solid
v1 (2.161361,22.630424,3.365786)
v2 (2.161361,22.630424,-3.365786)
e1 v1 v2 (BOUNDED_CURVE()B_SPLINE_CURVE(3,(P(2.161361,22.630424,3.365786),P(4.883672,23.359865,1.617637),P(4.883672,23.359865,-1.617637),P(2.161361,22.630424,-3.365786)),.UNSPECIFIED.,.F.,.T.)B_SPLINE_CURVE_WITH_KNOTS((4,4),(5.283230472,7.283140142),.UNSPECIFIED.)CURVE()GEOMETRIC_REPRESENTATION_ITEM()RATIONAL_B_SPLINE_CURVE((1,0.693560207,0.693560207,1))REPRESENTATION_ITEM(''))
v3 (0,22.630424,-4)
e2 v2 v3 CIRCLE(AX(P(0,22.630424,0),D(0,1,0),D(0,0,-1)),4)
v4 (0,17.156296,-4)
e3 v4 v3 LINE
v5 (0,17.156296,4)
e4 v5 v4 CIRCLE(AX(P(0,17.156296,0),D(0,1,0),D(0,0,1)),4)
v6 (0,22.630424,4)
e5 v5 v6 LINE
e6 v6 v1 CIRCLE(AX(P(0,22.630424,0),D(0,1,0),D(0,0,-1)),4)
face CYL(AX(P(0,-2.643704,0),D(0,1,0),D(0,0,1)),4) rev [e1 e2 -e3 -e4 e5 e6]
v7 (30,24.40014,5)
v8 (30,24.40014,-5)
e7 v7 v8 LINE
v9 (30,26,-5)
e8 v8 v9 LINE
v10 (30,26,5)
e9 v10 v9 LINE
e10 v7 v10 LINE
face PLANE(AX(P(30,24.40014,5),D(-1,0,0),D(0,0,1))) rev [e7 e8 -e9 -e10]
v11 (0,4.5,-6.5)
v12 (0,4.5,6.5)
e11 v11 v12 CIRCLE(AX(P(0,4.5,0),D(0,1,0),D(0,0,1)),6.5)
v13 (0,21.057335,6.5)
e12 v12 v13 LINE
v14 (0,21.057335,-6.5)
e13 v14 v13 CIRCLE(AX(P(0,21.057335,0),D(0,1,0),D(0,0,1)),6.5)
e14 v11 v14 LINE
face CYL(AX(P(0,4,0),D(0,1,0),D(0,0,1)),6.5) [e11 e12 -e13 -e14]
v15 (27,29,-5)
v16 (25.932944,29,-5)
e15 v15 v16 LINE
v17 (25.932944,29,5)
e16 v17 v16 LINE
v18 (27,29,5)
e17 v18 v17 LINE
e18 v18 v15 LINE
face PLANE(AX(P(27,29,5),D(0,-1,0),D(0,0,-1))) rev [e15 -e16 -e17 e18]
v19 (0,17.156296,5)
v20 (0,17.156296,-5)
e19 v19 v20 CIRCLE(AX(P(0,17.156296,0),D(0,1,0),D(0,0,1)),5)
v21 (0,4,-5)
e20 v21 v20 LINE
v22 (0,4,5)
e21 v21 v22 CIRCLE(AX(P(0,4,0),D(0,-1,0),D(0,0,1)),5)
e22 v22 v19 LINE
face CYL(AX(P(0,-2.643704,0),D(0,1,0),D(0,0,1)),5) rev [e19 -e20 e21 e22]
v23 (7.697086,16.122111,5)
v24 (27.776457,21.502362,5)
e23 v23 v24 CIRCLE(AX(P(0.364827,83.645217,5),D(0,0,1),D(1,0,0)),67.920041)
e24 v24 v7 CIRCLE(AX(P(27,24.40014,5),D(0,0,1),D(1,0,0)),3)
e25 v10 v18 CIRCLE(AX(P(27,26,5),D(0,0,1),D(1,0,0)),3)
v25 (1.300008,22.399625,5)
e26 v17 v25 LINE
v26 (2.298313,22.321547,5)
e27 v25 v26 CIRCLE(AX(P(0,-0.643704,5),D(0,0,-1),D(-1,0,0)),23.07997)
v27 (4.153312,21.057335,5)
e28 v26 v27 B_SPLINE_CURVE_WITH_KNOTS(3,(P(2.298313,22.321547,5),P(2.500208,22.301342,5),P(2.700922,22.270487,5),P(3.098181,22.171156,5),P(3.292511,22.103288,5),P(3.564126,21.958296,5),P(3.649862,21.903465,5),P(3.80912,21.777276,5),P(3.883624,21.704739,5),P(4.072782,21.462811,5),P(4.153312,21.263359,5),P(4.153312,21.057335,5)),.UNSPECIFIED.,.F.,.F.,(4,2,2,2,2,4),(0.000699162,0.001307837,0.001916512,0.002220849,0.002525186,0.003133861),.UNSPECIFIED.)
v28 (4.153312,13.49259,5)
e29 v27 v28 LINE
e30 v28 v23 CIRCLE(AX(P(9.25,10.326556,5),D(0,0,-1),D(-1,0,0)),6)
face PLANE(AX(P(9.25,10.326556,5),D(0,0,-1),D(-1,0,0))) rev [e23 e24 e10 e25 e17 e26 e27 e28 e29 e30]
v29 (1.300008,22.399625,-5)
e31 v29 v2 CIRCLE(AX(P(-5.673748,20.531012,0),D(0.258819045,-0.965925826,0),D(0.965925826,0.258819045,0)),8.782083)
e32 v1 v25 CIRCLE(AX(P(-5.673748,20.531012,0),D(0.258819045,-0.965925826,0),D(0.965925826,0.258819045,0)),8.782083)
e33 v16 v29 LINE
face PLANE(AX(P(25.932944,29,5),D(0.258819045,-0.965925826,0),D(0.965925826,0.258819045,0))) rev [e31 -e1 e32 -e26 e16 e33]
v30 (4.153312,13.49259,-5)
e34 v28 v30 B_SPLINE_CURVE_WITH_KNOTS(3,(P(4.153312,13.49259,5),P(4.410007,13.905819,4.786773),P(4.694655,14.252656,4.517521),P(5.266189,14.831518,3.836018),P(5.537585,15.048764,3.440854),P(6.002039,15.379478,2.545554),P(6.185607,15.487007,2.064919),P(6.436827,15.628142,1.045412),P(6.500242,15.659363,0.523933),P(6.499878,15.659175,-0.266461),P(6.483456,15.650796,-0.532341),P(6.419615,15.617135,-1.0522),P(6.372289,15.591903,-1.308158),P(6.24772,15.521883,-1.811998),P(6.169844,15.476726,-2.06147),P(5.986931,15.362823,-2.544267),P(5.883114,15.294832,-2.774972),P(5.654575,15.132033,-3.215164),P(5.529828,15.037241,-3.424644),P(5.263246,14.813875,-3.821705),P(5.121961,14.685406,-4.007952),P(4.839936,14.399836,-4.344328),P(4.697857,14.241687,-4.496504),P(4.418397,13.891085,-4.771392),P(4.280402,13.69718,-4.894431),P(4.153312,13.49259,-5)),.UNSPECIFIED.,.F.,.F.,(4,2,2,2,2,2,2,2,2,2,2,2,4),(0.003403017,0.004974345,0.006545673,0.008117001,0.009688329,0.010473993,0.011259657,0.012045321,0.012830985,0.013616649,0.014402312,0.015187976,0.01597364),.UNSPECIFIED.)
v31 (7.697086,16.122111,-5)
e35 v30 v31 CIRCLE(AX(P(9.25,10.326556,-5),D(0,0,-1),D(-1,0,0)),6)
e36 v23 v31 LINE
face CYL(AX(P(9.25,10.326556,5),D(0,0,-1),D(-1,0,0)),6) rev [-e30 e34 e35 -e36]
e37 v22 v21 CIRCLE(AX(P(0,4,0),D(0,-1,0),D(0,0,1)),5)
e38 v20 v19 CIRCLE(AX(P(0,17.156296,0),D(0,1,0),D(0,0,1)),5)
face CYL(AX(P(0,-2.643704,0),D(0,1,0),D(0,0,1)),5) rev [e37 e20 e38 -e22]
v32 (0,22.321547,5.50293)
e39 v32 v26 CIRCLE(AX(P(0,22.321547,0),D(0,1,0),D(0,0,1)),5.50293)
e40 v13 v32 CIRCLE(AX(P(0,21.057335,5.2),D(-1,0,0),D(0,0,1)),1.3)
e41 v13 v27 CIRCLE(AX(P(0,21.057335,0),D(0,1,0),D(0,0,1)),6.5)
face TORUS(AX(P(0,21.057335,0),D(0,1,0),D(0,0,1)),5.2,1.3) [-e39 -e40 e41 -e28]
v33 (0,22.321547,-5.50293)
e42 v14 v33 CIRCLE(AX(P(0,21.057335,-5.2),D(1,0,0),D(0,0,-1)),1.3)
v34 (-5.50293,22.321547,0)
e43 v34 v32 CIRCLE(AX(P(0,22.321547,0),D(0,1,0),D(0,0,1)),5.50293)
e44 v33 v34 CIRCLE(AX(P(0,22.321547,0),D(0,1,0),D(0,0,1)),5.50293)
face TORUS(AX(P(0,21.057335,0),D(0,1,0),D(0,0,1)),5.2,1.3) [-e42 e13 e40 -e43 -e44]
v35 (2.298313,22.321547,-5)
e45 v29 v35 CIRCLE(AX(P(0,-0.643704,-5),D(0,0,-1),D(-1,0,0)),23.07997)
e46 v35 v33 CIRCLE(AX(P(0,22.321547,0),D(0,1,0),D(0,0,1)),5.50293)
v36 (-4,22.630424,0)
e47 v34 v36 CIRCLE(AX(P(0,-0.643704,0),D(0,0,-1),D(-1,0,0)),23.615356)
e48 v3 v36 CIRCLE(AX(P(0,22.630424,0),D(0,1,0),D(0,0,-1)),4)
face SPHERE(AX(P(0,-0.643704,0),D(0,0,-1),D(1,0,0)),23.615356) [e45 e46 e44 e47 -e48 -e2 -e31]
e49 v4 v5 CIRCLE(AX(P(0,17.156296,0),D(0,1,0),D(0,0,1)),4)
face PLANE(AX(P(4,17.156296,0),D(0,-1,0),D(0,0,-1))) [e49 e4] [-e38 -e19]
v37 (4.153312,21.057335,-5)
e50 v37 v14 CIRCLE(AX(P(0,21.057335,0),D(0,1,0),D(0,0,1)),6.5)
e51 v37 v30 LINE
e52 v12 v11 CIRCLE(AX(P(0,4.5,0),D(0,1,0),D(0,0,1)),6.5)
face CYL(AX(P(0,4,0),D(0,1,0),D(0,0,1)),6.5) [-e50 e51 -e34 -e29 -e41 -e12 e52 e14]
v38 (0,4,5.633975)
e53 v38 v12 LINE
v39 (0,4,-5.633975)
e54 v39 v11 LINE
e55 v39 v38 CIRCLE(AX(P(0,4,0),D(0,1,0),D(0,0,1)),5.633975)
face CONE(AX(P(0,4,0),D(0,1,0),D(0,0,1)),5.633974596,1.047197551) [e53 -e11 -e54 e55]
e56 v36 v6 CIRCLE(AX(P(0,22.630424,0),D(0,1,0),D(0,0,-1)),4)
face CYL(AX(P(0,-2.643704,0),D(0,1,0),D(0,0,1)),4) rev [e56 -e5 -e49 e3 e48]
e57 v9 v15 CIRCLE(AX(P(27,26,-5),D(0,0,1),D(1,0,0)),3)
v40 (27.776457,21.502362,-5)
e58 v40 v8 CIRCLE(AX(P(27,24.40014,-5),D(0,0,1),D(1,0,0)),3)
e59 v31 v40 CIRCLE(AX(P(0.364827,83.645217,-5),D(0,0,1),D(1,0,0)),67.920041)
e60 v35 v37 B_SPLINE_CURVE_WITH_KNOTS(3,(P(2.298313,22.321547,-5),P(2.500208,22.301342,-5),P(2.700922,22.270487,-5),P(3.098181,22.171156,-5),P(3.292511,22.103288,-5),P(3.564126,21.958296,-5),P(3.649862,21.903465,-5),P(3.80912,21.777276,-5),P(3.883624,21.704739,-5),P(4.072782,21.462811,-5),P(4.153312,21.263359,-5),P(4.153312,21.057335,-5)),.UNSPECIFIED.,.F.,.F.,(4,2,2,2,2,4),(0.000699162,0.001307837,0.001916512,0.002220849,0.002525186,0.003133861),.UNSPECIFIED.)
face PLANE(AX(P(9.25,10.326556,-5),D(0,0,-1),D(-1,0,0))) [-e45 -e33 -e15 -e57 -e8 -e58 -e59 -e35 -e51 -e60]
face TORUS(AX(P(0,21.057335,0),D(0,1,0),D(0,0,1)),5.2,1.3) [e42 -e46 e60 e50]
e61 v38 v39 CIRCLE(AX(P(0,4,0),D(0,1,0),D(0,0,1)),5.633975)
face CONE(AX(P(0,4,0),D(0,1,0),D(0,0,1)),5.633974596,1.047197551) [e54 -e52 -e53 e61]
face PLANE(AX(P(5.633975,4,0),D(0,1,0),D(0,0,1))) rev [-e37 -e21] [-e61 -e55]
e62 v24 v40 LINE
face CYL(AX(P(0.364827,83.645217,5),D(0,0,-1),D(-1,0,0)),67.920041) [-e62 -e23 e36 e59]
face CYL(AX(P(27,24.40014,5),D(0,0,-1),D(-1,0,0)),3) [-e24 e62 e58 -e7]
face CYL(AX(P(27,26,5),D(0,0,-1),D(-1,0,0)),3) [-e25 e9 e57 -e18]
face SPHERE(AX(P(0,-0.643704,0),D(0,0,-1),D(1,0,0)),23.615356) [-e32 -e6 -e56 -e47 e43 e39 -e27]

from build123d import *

# Parameters (mm, degrees)
EXTRUDE_1_DEPTH      = 5
EXTRUDE_1_DEPTH_BACK = 5


with BuildPart() as part:
    # 草图2 → 旋转1 (revolve)
    with BuildSketch(Plane.XY, mode=Mode.PRIVATE) as revolve_1_sk:
        with BuildLine():
            Line((6.5, 21.057334971), (6.5, 4.5))
            Line((6.5, 4.5), (5.633974596, 4))
            Line((5.633974596, 4), (0, 4))
            Line((0, 4), (0, 22.97165153))
            ThreePointArc((0, 22.97165153), (2.770599147, 22.808562355), (5.502930419, 22.321547438))
            ThreePointArc((5.502930419, 22.321547438), (6.220737367, 21.862378589), (6.5, 21.057334971))
        make_face()
    revolve(revolve_1_sk.sketch.rotate(Axis((0, 4, 0), (0, 1, 0)), 270), axis=Axis((0, 4, 0), (0, 1, 0)))

    # 草图1 → 凸台-拉伸1 (add, two sides: drawn at the far end of the back side and taken through both)
    with BuildSketch(Plane.XY.offset(-EXTRUDE_1_DEPTH_BACK)):
        with BuildLine():
            Line((-3.333333333, 5.5), (3.25, 5.5))
            Line((3.25, 5.5), (3.25, 10.326555972))
            ThreePointArc((3.25, 10.326555972), (4.489879958, 13.979124546), (7.697085729, 16.12211093))
            ThreePointArc((7.697085729, 16.12211093), (17.943826668, 18.039495945), (27.776457135, 21.502362282))
            ThreePointArc((27.776457135, 21.502362282), (29.380060021, 22.573855474), (30, 24.400139761))
            Line((30, 24.400139761), (30, 26))
            ThreePointArc((30, 26), (29.121320344, 28.121320344), (27, 29))
            Line((27, 29), (25.932943889, 29))
            Line((25.932943889, 29), (-3.333333333, 21.158124653))
            Line((-3.333333333, 21.158124653), (-3.333333333, 5.5))
        make_face()
    extrude(amount=EXTRUDE_1_DEPTH + EXTRUDE_1_DEPTH_BACK)

    # 草图3 → 切除-旋转1 (revolve, cut)
    with BuildSketch(Plane.XY, mode=Mode.PRIVATE) as cut_revolve_1_sk:
        Polygon((0, 28.156296), (4, 28.156296), (4, 17.156296), (5, 17.156296), (5, -2.643704), (0, -2.643704), align=None)
    revolve(cut_revolve_1_sk.sketch.rotate(Axis((0, -2.643704, 0), (0, 1, 0)), 270), axis=Axis((0, -2.643704, 0), (0, 1, 0)), mode=Mode.SUBTRACT)


solid = part.part
